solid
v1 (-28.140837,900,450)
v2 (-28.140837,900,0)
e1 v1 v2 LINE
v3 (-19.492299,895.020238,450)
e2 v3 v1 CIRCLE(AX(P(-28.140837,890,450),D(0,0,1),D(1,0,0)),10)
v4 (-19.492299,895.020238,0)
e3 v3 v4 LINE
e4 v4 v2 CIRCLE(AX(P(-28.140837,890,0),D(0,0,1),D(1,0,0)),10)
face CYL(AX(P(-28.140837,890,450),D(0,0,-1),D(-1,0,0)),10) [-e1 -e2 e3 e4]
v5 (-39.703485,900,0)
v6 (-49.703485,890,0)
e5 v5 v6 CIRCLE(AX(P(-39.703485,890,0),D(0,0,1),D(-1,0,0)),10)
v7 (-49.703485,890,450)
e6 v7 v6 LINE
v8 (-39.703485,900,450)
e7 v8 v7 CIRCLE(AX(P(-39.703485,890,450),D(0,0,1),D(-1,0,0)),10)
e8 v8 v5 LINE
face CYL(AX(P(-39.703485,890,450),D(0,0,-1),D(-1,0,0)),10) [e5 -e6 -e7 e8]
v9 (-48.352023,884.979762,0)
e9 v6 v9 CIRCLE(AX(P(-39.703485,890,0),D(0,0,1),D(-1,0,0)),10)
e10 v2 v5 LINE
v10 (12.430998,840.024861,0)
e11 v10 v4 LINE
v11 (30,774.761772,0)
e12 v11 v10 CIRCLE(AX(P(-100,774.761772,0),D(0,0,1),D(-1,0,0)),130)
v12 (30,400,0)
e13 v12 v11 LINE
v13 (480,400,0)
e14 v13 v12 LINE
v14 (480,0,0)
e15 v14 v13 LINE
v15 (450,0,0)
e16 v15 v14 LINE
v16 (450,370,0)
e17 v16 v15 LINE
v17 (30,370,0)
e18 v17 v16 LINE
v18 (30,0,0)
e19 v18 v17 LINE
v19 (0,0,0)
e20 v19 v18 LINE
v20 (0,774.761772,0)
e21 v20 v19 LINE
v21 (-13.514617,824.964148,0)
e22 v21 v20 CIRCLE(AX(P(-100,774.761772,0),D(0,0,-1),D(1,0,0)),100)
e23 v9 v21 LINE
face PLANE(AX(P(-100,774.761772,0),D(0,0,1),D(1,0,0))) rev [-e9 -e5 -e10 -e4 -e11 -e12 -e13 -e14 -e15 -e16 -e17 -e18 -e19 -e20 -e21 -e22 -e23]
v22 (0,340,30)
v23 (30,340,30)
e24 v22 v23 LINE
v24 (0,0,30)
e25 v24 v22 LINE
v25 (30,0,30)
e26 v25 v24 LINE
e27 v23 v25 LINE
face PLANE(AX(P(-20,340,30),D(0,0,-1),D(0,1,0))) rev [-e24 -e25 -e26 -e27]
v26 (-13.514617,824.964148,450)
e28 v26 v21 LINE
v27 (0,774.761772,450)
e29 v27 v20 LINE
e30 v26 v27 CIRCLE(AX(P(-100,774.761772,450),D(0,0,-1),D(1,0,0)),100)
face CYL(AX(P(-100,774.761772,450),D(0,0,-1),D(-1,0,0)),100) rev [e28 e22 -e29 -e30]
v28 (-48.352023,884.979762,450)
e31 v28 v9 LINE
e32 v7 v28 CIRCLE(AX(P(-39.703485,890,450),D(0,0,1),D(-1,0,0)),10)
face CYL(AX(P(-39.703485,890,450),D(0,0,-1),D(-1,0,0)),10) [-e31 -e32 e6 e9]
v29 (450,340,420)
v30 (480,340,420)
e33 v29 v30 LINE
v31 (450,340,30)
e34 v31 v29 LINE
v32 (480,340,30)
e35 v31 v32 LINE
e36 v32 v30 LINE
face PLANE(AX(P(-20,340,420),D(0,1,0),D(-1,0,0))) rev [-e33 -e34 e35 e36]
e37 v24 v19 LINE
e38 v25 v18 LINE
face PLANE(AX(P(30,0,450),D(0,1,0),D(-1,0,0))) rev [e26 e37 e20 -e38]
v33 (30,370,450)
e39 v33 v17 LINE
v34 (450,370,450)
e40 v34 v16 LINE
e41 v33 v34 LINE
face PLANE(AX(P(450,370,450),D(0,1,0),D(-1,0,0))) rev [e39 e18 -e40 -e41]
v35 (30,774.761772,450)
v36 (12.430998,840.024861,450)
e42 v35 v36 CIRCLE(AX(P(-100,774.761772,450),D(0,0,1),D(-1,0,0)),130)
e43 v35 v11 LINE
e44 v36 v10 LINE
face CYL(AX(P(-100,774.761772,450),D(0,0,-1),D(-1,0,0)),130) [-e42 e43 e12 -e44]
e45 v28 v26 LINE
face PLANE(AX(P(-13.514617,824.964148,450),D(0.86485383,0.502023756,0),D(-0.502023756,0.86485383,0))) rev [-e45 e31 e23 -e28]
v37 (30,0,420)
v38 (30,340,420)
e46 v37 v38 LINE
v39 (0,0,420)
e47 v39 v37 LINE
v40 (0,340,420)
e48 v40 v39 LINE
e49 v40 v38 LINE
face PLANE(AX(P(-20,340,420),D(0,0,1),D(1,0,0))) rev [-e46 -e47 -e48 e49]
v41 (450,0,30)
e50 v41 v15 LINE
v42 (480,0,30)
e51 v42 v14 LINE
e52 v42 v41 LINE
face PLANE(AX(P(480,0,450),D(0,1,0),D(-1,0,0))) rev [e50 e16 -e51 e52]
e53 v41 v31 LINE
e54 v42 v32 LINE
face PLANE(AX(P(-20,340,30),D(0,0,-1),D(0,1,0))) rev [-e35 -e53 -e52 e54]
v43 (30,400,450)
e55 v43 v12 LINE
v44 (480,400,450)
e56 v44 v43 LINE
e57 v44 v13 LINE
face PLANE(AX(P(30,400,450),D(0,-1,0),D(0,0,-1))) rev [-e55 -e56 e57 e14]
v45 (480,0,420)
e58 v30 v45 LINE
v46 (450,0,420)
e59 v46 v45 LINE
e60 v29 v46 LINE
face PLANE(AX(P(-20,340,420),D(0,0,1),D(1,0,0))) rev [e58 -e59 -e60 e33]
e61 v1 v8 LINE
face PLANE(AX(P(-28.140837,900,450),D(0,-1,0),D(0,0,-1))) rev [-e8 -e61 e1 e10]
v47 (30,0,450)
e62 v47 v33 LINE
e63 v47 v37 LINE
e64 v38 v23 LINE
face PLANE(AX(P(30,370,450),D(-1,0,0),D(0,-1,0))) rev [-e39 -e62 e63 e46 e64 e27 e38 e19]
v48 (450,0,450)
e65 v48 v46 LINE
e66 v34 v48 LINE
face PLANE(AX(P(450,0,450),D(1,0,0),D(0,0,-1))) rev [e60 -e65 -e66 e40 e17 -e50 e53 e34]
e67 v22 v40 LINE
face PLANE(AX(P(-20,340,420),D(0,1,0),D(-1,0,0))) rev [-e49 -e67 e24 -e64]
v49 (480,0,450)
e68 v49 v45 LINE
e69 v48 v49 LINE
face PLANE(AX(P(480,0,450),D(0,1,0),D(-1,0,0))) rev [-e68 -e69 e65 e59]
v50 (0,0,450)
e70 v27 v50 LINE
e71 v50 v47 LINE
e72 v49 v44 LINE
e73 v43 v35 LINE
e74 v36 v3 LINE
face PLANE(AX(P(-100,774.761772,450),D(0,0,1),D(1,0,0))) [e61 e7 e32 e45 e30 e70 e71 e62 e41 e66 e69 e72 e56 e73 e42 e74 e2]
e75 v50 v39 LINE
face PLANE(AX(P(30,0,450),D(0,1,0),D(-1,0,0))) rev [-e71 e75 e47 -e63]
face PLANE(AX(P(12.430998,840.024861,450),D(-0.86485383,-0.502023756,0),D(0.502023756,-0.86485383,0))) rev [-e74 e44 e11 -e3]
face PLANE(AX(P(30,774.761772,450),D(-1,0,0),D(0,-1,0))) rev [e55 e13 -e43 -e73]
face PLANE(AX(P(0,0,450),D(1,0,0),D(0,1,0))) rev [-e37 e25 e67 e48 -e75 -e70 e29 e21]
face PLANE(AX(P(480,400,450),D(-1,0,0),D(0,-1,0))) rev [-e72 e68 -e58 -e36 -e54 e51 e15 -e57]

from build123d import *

# Parameters (mm, degrees)
BOSS_EXTRUDE1_DEPTH = 450
SKETCH2_W           = 390
SKETCH2_H           = 365.797461664
CUT_EXTRUDE1_DEPTH  = 500


with BuildPart() as part:
    # Sketch1 → Boss-Extrude1 (new body)
    with BuildSketch(Plane.XY):
        with BuildLine():
            Line((0, 0), (0, 774.761772336))
            ThreePointArc((0, 774.761772336), (-3.437744681, 800.756595814), (-13.514616953, 824.964147969))
            Line((-13.514616953, 824.964147969), (-48.352023173, 884.979762437))
            ThreePointArc((-48.352023173, 884.979762437), (-48.369579018, 894.989870959), (-39.703484868, 900))
            Line((-39.703484868, 900), (-28.140837346, 900))
            ThreePointArc((-28.140837346, 900), (-23.150966388, 898.66609415), (-19.492299041, 895.020237563))
            Line((-19.492299041, 895.020237563), (12.430997961, 840.024860659))
            ThreePointArc((12.430997961, 840.024860659), (25.530931915, 808.555042857), (30, 774.761772336))
            Line((30, 774.761772336), (30, 400))
            Line((30, 400), (480, 400))
            Line((480, 400), (480, 0))
            Line((480, 0), (450, 0))
            Line((450, 0), (450, 370))
            Line((450, 370), (30, 370))
            Line((30, 370), (30, 0))
            Line((30, 0), (0, 0))
        make_face()
    extrude(amount=BOSS_EXTRUDE1_DEPTH)

    # Sketch2 → Cut-Extrude1 (cut)
    with BuildSketch(Plane(origin=(480, 0, 0), x_dir=(0, 0, -1), z_dir=(1, 0, 0))):
        with Locations((-225, 157.101269168)):
            Rectangle(SKETCH2_W, SKETCH2_H)
    extrude(amount=-CUT_EXTRUDE1_DEPTH, mode=Mode.SUBTRACT)


solid = part.part
